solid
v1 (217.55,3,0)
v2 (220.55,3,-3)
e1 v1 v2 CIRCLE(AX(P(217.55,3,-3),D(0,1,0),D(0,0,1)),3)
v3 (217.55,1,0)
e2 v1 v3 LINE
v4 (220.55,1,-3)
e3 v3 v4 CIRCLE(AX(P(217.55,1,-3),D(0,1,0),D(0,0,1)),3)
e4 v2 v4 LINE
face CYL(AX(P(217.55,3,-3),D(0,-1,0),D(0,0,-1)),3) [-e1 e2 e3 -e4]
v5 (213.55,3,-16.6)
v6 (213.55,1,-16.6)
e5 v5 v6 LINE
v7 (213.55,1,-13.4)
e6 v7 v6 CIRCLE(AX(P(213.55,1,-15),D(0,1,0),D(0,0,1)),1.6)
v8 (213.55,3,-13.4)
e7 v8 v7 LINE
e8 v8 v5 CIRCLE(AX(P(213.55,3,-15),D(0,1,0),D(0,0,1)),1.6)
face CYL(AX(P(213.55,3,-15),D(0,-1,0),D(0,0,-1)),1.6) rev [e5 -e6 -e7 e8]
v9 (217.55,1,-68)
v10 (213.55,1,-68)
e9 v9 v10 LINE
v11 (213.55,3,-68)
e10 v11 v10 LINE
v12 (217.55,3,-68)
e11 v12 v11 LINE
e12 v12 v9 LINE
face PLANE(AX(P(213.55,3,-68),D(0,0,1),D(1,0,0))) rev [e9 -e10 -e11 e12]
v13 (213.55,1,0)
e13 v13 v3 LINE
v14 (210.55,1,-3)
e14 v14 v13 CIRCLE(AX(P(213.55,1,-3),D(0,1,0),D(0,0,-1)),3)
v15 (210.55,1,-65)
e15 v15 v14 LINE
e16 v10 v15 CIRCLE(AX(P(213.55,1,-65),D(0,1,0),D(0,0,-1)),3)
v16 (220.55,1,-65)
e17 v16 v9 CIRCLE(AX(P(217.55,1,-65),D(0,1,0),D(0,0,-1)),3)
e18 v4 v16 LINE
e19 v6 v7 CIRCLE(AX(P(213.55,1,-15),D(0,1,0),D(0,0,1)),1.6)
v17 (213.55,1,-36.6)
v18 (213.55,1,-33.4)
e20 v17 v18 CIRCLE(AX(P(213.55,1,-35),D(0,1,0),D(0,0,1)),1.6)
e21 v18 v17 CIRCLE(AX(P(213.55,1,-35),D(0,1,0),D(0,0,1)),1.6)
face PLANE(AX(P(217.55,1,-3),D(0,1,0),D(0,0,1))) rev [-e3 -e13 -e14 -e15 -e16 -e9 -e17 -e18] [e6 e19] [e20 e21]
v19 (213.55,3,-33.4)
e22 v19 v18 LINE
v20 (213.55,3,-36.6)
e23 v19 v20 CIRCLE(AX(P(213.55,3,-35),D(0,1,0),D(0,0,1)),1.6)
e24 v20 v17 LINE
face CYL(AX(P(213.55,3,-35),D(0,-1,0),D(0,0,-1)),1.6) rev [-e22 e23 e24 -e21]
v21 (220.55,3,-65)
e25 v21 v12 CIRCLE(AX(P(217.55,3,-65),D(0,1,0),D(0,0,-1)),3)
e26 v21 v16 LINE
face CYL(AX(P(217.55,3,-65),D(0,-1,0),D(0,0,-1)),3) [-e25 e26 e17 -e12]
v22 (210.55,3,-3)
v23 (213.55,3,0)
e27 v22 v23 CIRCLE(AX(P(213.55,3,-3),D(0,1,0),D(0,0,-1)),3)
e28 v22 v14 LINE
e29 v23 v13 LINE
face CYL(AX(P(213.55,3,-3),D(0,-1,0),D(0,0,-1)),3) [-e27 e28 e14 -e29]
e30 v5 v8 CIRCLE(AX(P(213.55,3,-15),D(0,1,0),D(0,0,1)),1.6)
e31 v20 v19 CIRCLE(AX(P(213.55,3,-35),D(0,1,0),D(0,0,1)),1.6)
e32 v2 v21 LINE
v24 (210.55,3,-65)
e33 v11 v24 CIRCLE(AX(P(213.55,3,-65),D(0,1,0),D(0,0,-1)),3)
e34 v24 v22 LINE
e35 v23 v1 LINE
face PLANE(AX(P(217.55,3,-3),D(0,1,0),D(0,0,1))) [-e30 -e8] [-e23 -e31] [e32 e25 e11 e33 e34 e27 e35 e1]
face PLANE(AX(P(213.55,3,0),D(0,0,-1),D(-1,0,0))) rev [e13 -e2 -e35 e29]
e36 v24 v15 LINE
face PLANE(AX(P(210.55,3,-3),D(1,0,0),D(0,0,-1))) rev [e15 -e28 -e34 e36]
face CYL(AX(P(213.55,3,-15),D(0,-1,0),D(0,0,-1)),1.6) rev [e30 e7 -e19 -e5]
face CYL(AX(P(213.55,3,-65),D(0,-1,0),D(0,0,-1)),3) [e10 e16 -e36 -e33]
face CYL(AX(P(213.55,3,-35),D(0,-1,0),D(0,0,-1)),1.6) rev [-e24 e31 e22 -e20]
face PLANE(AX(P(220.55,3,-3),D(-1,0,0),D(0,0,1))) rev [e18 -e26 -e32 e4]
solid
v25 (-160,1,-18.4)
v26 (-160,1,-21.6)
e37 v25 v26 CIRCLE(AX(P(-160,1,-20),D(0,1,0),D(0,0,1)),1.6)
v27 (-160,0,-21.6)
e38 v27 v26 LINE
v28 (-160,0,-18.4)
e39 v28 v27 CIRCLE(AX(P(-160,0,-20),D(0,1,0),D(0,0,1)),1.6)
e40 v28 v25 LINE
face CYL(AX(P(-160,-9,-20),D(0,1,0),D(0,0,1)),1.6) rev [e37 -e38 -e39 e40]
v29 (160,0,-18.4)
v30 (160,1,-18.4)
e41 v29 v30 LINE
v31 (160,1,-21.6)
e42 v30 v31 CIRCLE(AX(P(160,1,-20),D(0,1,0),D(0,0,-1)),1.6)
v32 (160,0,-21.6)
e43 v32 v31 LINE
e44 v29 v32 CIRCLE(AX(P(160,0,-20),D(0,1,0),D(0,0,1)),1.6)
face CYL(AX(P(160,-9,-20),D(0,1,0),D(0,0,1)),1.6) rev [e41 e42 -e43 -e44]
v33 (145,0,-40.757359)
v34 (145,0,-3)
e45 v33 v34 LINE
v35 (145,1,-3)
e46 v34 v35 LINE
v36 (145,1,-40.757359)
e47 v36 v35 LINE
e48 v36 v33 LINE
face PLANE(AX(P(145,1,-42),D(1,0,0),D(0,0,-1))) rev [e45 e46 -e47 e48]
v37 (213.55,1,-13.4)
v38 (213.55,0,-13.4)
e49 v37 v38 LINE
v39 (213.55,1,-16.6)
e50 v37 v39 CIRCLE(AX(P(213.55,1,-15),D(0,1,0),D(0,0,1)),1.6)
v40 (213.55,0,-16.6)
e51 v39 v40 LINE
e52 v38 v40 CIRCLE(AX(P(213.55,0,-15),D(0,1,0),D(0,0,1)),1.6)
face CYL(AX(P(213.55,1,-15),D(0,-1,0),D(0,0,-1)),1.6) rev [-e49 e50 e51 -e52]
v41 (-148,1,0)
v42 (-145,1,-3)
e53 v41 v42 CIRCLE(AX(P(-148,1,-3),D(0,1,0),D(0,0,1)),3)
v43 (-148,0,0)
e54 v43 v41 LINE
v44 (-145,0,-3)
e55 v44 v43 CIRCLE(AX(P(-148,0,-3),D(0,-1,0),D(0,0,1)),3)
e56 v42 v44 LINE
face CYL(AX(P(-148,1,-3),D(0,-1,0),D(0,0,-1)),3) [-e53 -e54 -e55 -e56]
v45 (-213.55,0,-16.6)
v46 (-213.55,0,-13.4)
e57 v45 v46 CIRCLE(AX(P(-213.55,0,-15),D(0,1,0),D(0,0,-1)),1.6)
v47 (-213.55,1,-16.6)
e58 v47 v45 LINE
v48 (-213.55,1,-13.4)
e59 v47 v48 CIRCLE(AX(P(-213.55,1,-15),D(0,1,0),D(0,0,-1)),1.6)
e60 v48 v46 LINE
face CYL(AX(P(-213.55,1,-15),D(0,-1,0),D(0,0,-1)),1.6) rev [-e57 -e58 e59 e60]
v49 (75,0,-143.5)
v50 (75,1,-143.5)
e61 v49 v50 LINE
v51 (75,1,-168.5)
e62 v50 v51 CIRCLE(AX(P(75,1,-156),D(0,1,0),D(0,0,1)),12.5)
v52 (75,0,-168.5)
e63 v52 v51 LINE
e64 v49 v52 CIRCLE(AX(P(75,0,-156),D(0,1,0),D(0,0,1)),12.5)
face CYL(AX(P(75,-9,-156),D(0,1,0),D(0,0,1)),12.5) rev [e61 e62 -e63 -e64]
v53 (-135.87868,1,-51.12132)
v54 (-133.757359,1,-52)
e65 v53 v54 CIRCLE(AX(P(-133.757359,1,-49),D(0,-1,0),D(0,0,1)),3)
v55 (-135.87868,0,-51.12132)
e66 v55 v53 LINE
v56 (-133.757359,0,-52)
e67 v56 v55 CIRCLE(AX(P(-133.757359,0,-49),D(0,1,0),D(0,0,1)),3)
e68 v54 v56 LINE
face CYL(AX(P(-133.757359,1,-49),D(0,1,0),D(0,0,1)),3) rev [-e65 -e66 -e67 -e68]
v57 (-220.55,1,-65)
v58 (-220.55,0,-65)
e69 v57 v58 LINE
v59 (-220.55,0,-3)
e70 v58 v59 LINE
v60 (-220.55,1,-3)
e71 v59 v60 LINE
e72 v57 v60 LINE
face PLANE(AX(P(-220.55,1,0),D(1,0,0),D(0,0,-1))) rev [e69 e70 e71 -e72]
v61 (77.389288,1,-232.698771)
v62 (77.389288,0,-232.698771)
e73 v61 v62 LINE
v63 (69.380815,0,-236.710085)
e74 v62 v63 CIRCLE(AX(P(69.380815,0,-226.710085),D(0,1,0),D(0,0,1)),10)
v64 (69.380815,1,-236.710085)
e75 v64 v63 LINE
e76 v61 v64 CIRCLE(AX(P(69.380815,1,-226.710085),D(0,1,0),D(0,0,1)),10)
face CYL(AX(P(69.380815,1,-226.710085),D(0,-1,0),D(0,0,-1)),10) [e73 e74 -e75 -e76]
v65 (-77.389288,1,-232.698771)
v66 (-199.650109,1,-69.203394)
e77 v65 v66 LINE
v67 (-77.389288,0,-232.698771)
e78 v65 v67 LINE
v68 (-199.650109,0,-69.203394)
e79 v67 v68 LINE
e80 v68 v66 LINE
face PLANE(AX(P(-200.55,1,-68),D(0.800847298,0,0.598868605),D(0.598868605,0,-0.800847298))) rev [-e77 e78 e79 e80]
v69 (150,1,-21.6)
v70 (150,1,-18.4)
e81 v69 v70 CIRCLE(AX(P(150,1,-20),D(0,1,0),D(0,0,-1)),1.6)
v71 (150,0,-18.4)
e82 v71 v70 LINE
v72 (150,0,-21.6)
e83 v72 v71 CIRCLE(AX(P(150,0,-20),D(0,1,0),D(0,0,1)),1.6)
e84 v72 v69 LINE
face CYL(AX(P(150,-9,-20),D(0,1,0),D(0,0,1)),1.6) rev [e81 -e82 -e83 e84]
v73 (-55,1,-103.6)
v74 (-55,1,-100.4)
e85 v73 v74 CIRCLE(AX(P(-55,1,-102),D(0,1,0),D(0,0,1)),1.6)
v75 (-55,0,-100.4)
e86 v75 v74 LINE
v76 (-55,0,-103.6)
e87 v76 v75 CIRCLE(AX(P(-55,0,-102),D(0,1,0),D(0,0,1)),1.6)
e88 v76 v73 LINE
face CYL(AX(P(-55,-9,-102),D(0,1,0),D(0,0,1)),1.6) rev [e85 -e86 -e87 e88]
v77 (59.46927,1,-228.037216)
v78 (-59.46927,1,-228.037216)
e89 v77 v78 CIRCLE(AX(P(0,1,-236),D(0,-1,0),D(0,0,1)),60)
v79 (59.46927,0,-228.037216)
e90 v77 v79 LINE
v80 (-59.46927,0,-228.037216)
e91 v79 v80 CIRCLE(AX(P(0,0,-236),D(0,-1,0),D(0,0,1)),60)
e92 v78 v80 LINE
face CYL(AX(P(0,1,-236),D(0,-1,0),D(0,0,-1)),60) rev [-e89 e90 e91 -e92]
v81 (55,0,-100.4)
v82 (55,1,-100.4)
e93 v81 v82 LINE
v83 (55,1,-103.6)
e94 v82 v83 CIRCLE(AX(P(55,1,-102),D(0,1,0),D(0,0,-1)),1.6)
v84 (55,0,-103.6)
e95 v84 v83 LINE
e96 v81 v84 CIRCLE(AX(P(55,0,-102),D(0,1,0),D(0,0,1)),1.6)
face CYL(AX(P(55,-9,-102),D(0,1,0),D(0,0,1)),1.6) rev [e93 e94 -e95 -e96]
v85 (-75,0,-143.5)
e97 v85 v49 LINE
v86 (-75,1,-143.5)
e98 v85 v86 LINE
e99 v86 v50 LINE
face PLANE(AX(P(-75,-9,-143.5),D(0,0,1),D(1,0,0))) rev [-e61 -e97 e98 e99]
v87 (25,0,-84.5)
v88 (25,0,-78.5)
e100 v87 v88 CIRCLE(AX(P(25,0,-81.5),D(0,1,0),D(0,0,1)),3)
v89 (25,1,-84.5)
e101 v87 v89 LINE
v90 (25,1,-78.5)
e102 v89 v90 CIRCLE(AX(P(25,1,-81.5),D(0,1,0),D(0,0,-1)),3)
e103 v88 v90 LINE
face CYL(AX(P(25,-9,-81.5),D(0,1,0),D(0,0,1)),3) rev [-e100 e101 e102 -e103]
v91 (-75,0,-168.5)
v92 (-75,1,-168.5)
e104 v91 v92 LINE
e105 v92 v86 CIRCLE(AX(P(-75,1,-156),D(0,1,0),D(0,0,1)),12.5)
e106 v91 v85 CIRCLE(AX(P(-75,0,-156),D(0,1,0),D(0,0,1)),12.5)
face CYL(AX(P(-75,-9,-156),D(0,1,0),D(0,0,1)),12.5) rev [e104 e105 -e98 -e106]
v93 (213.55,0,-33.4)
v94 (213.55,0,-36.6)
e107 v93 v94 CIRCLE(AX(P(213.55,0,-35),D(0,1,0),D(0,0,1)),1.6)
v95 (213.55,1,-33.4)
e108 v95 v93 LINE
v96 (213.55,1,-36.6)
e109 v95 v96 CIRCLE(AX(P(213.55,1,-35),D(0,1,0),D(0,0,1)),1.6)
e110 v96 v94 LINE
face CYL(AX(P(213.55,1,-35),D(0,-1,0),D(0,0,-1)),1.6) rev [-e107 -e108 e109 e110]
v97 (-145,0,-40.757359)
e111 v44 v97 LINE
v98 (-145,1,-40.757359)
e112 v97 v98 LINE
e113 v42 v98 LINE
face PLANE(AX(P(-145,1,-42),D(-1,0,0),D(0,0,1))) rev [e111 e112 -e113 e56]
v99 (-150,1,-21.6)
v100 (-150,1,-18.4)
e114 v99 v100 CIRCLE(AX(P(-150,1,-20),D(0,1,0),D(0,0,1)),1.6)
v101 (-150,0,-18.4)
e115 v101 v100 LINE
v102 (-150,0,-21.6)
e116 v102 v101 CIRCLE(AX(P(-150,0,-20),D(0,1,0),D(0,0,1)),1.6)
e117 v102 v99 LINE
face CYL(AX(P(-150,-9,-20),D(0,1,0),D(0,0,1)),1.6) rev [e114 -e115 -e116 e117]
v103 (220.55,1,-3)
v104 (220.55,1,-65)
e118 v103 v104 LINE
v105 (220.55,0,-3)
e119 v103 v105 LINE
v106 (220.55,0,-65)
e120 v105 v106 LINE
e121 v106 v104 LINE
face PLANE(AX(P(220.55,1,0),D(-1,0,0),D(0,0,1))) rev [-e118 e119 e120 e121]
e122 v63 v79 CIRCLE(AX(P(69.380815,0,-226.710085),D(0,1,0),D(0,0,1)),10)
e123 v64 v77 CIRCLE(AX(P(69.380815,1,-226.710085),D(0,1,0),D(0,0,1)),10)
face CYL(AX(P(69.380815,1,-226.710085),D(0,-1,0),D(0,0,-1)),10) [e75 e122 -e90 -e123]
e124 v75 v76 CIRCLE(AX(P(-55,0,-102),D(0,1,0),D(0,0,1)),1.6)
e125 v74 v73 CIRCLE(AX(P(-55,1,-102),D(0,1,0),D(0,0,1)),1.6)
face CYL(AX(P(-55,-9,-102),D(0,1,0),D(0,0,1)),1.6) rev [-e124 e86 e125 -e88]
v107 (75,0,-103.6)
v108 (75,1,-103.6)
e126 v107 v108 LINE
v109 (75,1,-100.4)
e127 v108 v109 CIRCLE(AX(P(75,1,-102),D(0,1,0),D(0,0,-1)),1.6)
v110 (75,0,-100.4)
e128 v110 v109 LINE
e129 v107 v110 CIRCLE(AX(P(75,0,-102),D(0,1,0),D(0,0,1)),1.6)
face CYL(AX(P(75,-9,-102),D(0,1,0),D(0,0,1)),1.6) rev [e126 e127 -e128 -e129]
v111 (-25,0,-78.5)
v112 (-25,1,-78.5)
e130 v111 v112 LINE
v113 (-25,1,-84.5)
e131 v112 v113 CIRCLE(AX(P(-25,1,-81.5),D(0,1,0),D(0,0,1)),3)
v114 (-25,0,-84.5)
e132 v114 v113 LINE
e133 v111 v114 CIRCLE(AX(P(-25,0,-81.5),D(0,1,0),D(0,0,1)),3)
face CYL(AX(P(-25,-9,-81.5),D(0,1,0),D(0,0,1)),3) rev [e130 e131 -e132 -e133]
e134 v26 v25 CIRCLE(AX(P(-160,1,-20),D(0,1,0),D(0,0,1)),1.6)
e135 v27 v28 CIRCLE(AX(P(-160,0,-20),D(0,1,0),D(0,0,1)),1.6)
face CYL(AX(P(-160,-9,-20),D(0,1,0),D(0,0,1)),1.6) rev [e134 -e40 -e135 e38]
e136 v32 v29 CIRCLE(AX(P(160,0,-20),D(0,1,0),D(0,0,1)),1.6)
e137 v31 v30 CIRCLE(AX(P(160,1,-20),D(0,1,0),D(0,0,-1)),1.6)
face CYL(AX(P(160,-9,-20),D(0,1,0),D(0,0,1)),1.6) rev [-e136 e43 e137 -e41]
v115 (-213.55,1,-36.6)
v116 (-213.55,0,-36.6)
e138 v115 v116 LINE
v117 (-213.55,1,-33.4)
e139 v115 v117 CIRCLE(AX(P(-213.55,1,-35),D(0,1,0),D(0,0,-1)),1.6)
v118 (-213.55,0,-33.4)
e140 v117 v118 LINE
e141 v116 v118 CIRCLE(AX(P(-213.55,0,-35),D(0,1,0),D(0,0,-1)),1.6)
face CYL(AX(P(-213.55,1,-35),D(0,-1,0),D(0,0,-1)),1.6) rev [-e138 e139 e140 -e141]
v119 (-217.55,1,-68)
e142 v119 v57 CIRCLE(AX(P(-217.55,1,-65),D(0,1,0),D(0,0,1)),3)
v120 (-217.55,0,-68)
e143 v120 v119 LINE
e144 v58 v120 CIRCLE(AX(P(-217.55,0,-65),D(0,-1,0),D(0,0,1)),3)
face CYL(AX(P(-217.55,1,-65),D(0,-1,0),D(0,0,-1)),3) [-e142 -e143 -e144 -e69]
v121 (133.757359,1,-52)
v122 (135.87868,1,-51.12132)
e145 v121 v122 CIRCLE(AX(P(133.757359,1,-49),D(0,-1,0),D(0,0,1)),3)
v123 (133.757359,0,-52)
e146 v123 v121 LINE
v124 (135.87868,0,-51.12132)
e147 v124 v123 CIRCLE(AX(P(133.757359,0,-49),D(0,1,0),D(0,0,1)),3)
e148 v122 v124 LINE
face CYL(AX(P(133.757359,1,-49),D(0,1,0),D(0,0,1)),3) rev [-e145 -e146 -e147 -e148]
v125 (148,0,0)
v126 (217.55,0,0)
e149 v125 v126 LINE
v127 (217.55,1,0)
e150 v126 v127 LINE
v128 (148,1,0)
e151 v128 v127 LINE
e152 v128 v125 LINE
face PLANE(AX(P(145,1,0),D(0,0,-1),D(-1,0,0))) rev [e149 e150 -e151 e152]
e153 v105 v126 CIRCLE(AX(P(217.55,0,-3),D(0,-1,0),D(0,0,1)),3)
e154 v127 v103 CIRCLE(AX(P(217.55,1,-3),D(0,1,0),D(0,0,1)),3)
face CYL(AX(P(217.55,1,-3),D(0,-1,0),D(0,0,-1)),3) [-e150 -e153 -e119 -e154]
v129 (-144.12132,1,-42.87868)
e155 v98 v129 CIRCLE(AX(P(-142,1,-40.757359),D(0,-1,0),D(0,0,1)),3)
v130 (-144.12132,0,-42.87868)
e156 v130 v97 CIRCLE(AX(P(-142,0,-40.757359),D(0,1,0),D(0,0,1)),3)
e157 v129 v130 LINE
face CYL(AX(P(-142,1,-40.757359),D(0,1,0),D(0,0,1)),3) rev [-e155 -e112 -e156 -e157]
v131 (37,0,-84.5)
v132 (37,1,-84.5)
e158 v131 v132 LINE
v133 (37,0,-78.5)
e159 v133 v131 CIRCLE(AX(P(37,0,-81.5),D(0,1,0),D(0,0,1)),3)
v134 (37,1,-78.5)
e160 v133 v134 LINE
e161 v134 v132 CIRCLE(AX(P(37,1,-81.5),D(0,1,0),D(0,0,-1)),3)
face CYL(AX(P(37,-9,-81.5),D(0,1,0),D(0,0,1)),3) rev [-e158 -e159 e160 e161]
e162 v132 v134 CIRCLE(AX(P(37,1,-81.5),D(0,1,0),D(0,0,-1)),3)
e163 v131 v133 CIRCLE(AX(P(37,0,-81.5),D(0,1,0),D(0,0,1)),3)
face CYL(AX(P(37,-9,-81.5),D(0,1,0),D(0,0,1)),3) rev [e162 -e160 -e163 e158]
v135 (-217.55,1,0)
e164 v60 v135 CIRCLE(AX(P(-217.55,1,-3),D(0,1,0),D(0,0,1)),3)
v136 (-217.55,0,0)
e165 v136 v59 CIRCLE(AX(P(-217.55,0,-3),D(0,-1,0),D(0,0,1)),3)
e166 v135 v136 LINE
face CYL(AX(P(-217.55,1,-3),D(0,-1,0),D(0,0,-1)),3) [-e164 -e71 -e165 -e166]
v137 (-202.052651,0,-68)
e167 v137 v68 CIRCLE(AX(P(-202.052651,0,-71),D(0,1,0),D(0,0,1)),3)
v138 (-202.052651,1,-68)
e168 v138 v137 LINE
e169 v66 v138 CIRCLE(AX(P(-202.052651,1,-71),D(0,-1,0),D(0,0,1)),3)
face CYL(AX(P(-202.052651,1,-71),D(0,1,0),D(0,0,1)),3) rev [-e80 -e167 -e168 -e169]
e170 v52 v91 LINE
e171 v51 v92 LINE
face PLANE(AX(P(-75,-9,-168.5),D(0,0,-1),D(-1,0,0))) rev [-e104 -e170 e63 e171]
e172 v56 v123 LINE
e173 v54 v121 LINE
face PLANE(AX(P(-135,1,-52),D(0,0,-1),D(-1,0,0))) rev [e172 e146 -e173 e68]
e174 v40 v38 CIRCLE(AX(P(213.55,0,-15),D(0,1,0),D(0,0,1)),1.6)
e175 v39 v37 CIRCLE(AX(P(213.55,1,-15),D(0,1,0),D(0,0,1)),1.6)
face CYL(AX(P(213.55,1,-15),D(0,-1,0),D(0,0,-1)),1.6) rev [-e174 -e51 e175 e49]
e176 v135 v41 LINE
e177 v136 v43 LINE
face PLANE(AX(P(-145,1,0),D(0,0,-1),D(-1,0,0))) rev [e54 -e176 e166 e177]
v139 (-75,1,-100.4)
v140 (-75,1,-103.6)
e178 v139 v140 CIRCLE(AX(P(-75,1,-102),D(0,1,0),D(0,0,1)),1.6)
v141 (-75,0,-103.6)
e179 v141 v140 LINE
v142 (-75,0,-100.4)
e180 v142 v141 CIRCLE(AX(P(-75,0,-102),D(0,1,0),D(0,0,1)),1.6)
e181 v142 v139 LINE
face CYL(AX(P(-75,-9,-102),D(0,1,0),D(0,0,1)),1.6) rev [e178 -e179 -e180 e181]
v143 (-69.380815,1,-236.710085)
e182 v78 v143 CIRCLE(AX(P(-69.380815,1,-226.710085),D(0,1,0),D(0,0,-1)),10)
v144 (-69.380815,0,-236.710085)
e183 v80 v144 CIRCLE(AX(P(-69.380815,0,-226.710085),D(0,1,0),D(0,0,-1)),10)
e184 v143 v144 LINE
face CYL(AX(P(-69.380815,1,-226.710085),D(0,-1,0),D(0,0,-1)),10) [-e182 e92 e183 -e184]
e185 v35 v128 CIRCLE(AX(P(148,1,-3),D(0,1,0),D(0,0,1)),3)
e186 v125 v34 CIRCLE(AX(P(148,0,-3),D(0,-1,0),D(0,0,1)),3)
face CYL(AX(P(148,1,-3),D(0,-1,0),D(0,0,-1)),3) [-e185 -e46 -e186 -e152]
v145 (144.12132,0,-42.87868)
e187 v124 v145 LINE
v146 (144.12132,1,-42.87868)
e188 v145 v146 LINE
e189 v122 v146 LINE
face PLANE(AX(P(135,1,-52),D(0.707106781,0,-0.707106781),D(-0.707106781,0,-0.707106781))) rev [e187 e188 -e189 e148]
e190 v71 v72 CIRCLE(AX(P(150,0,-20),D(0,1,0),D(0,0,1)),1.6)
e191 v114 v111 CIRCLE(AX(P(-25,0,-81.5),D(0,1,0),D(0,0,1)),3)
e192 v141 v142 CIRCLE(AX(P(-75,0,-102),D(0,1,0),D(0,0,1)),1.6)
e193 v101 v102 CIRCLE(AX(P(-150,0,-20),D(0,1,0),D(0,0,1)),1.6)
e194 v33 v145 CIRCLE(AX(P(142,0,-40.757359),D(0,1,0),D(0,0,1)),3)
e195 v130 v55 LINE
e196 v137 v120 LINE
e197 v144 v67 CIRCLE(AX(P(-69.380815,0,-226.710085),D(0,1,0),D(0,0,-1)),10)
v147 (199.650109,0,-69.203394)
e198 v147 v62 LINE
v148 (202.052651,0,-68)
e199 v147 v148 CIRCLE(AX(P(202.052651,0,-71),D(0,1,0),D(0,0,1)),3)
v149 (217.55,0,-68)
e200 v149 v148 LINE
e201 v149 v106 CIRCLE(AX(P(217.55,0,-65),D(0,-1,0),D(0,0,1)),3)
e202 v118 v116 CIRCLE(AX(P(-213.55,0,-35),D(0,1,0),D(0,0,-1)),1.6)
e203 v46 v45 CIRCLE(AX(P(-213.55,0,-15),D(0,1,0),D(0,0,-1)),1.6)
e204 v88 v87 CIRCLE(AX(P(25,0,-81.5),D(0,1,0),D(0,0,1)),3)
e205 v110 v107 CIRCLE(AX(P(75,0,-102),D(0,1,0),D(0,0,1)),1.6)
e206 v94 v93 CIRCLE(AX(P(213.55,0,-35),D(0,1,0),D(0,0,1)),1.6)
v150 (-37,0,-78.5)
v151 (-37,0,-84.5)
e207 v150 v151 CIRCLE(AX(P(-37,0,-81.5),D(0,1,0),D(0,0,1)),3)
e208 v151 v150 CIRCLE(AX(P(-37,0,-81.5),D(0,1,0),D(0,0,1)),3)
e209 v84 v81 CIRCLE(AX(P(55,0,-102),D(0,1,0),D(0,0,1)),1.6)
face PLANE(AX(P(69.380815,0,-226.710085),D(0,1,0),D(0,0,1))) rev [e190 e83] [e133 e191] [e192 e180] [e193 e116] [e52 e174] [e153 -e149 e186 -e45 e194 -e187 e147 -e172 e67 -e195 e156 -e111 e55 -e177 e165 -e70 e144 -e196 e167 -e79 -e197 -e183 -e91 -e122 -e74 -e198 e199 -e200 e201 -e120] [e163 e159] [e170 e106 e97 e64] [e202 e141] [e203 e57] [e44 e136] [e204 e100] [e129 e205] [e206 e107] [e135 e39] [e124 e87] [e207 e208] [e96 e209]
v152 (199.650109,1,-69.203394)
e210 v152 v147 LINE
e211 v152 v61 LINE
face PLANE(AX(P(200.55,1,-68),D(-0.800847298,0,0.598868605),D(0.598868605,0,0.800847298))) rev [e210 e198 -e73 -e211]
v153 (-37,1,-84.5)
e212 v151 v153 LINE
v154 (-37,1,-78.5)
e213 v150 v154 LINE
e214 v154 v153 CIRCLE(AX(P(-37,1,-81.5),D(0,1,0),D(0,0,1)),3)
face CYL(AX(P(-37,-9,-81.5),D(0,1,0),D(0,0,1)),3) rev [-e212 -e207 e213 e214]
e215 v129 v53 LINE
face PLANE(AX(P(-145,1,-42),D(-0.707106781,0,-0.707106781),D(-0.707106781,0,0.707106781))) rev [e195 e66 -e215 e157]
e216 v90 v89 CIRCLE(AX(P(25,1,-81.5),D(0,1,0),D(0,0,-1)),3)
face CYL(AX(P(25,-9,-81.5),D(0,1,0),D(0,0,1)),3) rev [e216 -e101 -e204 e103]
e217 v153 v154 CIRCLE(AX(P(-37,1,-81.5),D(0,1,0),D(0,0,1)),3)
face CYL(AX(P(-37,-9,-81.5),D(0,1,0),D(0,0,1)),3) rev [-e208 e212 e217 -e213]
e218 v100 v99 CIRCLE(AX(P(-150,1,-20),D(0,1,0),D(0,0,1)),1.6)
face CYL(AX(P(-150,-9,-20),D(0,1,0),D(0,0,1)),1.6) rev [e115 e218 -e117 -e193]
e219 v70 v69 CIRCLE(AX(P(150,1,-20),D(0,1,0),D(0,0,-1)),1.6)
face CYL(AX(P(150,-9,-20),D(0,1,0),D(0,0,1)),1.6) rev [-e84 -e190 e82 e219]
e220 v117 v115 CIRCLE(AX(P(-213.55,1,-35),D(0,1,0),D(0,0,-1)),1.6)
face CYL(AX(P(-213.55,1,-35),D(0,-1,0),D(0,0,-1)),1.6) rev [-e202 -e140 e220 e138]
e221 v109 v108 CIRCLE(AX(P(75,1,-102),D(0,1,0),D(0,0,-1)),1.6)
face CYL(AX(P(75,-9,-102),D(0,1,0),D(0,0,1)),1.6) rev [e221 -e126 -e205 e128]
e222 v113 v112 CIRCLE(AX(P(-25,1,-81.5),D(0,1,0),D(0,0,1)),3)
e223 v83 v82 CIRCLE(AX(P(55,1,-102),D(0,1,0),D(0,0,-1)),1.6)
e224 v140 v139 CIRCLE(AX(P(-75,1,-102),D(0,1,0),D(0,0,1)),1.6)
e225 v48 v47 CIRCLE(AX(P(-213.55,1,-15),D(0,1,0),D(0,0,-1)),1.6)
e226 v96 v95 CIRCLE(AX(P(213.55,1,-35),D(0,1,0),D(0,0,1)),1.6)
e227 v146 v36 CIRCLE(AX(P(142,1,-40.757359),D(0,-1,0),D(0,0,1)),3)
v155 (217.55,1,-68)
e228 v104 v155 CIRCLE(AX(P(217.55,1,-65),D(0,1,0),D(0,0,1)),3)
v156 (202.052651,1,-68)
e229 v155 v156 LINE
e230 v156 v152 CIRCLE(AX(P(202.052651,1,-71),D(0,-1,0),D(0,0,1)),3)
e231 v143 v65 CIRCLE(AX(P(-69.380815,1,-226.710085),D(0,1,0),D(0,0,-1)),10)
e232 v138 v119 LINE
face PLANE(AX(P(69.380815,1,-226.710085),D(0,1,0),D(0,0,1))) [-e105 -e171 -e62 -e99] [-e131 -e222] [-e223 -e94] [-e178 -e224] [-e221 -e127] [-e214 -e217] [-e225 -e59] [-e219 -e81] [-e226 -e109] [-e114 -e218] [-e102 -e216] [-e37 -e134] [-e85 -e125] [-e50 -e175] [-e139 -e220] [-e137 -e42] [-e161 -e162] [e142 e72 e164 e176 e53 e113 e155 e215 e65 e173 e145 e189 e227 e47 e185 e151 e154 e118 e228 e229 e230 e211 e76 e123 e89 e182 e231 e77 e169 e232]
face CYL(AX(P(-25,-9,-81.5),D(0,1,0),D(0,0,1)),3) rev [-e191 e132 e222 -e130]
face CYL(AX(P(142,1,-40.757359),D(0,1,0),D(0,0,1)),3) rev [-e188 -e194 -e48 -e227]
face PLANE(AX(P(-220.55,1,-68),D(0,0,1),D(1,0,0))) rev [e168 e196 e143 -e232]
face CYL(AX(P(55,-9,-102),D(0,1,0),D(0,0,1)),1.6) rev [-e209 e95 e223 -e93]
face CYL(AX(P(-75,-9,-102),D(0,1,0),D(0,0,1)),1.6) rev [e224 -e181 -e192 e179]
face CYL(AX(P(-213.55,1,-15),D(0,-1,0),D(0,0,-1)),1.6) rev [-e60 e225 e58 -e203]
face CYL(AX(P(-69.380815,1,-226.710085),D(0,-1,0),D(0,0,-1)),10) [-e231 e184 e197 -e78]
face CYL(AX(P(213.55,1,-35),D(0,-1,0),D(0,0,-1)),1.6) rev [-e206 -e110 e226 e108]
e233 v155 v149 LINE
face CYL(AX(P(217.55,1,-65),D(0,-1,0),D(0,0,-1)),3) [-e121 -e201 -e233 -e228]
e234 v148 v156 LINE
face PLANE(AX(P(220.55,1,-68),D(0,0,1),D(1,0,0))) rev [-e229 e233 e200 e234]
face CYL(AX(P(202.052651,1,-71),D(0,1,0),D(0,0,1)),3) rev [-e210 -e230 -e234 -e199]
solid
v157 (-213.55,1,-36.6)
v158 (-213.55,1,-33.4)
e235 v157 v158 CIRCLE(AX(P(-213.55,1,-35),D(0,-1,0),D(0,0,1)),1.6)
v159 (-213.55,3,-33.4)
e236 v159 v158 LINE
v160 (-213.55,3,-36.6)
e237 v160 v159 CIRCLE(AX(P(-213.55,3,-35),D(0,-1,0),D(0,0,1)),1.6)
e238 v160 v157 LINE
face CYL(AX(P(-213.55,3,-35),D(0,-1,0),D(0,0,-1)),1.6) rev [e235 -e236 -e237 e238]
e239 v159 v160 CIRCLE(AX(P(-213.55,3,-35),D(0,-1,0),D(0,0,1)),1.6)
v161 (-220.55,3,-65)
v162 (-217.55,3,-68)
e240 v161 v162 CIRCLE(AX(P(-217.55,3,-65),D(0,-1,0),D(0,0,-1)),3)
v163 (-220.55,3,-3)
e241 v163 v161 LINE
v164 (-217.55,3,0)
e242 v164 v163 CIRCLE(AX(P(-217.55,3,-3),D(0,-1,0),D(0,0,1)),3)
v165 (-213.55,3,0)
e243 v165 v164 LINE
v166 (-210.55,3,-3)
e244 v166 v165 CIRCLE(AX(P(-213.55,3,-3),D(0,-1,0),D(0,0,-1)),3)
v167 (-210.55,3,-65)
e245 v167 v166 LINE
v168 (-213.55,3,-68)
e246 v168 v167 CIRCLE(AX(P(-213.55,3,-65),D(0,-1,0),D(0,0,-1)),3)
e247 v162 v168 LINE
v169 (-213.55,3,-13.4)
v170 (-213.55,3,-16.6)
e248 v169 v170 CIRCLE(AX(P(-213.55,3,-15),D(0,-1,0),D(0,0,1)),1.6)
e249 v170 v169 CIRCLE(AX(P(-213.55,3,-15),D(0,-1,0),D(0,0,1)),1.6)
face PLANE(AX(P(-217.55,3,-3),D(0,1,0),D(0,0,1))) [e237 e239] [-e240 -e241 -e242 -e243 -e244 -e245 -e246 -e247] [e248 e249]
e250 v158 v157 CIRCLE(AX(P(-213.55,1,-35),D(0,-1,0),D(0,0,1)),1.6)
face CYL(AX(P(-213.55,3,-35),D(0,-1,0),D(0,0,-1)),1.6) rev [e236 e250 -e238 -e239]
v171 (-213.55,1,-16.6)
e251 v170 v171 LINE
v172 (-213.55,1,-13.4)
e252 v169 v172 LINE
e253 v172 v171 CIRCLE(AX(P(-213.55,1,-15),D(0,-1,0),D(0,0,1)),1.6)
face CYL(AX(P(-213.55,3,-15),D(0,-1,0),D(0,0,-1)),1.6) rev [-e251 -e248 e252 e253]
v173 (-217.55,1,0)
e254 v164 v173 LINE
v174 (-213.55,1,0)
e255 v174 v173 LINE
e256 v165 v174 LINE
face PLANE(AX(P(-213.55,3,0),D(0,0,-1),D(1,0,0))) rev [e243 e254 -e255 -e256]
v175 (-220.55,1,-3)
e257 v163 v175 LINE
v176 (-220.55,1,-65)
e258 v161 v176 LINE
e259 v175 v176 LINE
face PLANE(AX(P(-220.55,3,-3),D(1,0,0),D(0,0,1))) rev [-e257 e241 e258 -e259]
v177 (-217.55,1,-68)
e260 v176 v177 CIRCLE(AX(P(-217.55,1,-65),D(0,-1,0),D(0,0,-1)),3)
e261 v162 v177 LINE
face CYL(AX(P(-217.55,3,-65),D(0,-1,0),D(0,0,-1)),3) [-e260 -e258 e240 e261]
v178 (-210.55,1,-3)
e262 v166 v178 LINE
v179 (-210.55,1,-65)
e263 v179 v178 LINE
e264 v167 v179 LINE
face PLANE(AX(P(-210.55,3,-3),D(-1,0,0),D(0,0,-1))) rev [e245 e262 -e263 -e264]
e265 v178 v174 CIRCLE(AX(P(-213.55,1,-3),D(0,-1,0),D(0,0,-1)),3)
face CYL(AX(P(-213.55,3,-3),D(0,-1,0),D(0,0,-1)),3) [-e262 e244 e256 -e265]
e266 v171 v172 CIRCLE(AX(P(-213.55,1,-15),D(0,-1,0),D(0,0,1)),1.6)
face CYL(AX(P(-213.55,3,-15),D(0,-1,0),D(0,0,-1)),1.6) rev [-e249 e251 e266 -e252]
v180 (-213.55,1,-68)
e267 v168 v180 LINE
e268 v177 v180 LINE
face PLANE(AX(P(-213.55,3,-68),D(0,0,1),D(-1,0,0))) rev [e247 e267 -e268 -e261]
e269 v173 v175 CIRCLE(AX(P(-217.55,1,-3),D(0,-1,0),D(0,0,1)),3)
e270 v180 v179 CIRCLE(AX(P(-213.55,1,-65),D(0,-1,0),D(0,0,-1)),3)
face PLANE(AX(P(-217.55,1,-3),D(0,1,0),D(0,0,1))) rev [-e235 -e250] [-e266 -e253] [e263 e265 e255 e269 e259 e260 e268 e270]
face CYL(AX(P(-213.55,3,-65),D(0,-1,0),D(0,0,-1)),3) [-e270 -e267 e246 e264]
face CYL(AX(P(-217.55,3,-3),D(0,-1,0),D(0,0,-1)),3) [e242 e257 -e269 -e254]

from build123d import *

# Parameters (mm, degrees)
SKETCH_1_R          = 1.6
EXTRUDE_1_DEPTH     = 1
SKETCH_2_R          = 1.6
SKETCH_2_R_2        = 3
CUT_EXTRUDE_1_DEPTH = 10
FILLET_1_R          = 3
SKETCH_3_R          = 1.6
EXTRUDE_2_DEPTH     = 2


with BuildPart() as part:
    # 草图1 → 凸台-拉伸1 (new body)
    with BuildSketch(Plane(origin=(0, 0, 0), x_dir=(1, 0, 0), z_dir=(0, 1, 0))):
        with BuildLine():
            Line((-135, 52), (135, 52))
            Line((135, 52), (145, 42))
            Line((145, 42), (145, 0))
            Line((145, 0), (220.55, 0))
            Line((220.55, 0), (220.55, 68))
            Line((220.55, 68), (200.55, 68))
            Line((200.55, 68), (77.389287954, 232.698771447))
            ThreePointArc((77.389287954, 232.698771447), (66.863287332, 236.388001217), (59.469269979, 228.037216058))
            ThreePointArc((59.469269979, 228.037216058), (0, 176), (-59.469269979, 228.037216058))
            ThreePointArc((-59.469269979, 228.037216058), (-66.863287332, 236.388001217), (-77.389287954, 232.698771447))
            Line((-77.389287954, 232.698771447), (-200.55, 68))
            Line((-200.55, 68), (-220.55, 68))
            Line((-220.55, 68), (-220.55, 0))
            Line((-220.55, 0), (-145, 0))
            Line((-145, 0), (-145, 42))
            Line((-145, 42), (-135, 52))
        make_face()
        with Locations(Location((213.55, 35, 0), (0, 0, 270))):
            Circle(SKETCH_1_R, mode=Mode.SUBTRACT)
        with Locations(Location((-213.55, 35, 0), (0, 0, 90))):
            Circle(SKETCH_1_R, mode=Mode.SUBTRACT)
        with Locations(Location((213.55, 15, 0), (0, 0, 270))):
            Circle(SKETCH_1_R, mode=Mode.SUBTRACT)
        with Locations(Location((-213.55, 15, 0), (0, 0, 90))):
            Circle(SKETCH_1_R, mode=Mode.SUBTRACT)
    extrude(amount=EXTRUDE_1_DEPTH)

    # 草图2 → 切除-拉伸1 (cut)
    with BuildSketch(Plane(origin=(0, 1, 0), x_dir=(1, 0, 0), z_dir=(0, 1, 0))):
        with Locations(Location((-55, 102, 0), (0, 0, 270))):
            Circle(SKETCH_2_R)
        with Locations(Location((-75, 102, 0), (0, 0, 270))):
            Circle(SKETCH_2_R)
        with Locations(Location((75, 102, 0), (0, 0, 270))):
            Circle(SKETCH_2_R)
        with Locations(Location((55, 102, 0), (0, 0, 270))):
            Circle(SKETCH_2_R)
        with Locations(Location((-25, 81.5, 0), (0, 0, 270))):
            Circle(SKETCH_2_R_2)
        with Locations(Location((-37, 81.5, 0), (0, 0, 270))):
            Circle(SKETCH_2_R_2)
        with Locations(Location((37, 81.5, 0), (0, 0, 270))):
            Circle(SKETCH_2_R_2)
        with Locations(Location((25, 81.5, 0), (0, 0, 270))):
            Circle(SKETCH_2_R_2)
        with Locations(Location((-160, 20, 0), (0, 0, 270))):
            Circle(SKETCH_2_R)
        with Locations(Location((-150, 20, 0), (0, 0, 270))):
            Circle(SKETCH_2_R)
        with Locations(Location((150, 20, 0), (0, 0, 270))):
            Circle(SKETCH_2_R)
        with Locations(Location((160, 20, 0), (0, 0, 270))):
            Circle(SKETCH_2_R)
        with BuildLine():
            Line((-75, 168.5), (75, 168.5))
            ThreePointArc((75, 168.5), (87.5, 156), (75, 143.5))
            Line((75, 143.5), (-75, 143.5))
            ThreePointArc((-75, 143.5), (-87.5, 156), (-75, 168.5))
        make_face()
    extrude(amount=-CUT_EXTRUDE_1_DEPTH, mode=Mode.SUBTRACT)

    # 圆角1
    fillet_1_edges = [part.edges().sort_by_distance(p)[0] for p in [
        (145, 0.5, 0),
        (145, 0.5, -42),
        (135, 0.5, -52),
        (-135, 0.5, -52),
        (-145, 0.5, -42),
        (-145, 0.5, 0),
        (-220.55, 0.5, 0),
        (-220.55, 0.5, -68),
        (-200.55, 0.5, -68),
        (200.55, 0.5, -68),
        (220.55, 0.5, -68),
        (220.55, 0.5, 0),
    ]]
    fillet(fillet_1_edges, radius=FILLET_1_R)


with BuildPart() as body_2:
    # 草图3 → 凸台-拉伸2 (new body)
    with BuildSketch(Plane(origin=(0, 1, 0), x_dir=(1, 0, 0), z_dir=(0, 1, 0))):
        with BuildLine():
            Line((213.55, 0), (217.55, 0))
            ThreePointArc((217.55, 0), (219.671320344, 0.878679656), (220.55, 3))
            Line((220.55, 3), (220.55, 65))
            ThreePointArc((220.55, 65), (219.671320344, 67.121320344), (217.55, 68))
            Line((217.55, 68), (213.55, 68))
            ThreePointArc((213.55, 68), (211.428679656, 67.121320344), (210.55, 65))
            Line((210.55, 65), (210.55, 3))
            ThreePointArc((210.55, 3), (211.428679656, 0.878679656), (213.55, 0))
        make_face()
        with Locations(Location((213.55, 15, 0), (0, 0, 270))):
            Circle(SKETCH_3_R, mode=Mode.SUBTRACT)
        with Locations(Location((213.55, 35, 0), (0, 0, 270))):
            Circle(SKETCH_3_R, mode=Mode.SUBTRACT)
    extrude(amount=EXTRUDE_2_DEPTH)


with BuildPart() as body_3:
    # 镜向1: mirrored copy
    add(body_2.part.mirror(Plane(origin=(0, 0, 0), x_dir=(0, 0, 1), z_dir=(1, 0, 0))))


solid = Compound([part.part, body_2.part, body_3.part])
